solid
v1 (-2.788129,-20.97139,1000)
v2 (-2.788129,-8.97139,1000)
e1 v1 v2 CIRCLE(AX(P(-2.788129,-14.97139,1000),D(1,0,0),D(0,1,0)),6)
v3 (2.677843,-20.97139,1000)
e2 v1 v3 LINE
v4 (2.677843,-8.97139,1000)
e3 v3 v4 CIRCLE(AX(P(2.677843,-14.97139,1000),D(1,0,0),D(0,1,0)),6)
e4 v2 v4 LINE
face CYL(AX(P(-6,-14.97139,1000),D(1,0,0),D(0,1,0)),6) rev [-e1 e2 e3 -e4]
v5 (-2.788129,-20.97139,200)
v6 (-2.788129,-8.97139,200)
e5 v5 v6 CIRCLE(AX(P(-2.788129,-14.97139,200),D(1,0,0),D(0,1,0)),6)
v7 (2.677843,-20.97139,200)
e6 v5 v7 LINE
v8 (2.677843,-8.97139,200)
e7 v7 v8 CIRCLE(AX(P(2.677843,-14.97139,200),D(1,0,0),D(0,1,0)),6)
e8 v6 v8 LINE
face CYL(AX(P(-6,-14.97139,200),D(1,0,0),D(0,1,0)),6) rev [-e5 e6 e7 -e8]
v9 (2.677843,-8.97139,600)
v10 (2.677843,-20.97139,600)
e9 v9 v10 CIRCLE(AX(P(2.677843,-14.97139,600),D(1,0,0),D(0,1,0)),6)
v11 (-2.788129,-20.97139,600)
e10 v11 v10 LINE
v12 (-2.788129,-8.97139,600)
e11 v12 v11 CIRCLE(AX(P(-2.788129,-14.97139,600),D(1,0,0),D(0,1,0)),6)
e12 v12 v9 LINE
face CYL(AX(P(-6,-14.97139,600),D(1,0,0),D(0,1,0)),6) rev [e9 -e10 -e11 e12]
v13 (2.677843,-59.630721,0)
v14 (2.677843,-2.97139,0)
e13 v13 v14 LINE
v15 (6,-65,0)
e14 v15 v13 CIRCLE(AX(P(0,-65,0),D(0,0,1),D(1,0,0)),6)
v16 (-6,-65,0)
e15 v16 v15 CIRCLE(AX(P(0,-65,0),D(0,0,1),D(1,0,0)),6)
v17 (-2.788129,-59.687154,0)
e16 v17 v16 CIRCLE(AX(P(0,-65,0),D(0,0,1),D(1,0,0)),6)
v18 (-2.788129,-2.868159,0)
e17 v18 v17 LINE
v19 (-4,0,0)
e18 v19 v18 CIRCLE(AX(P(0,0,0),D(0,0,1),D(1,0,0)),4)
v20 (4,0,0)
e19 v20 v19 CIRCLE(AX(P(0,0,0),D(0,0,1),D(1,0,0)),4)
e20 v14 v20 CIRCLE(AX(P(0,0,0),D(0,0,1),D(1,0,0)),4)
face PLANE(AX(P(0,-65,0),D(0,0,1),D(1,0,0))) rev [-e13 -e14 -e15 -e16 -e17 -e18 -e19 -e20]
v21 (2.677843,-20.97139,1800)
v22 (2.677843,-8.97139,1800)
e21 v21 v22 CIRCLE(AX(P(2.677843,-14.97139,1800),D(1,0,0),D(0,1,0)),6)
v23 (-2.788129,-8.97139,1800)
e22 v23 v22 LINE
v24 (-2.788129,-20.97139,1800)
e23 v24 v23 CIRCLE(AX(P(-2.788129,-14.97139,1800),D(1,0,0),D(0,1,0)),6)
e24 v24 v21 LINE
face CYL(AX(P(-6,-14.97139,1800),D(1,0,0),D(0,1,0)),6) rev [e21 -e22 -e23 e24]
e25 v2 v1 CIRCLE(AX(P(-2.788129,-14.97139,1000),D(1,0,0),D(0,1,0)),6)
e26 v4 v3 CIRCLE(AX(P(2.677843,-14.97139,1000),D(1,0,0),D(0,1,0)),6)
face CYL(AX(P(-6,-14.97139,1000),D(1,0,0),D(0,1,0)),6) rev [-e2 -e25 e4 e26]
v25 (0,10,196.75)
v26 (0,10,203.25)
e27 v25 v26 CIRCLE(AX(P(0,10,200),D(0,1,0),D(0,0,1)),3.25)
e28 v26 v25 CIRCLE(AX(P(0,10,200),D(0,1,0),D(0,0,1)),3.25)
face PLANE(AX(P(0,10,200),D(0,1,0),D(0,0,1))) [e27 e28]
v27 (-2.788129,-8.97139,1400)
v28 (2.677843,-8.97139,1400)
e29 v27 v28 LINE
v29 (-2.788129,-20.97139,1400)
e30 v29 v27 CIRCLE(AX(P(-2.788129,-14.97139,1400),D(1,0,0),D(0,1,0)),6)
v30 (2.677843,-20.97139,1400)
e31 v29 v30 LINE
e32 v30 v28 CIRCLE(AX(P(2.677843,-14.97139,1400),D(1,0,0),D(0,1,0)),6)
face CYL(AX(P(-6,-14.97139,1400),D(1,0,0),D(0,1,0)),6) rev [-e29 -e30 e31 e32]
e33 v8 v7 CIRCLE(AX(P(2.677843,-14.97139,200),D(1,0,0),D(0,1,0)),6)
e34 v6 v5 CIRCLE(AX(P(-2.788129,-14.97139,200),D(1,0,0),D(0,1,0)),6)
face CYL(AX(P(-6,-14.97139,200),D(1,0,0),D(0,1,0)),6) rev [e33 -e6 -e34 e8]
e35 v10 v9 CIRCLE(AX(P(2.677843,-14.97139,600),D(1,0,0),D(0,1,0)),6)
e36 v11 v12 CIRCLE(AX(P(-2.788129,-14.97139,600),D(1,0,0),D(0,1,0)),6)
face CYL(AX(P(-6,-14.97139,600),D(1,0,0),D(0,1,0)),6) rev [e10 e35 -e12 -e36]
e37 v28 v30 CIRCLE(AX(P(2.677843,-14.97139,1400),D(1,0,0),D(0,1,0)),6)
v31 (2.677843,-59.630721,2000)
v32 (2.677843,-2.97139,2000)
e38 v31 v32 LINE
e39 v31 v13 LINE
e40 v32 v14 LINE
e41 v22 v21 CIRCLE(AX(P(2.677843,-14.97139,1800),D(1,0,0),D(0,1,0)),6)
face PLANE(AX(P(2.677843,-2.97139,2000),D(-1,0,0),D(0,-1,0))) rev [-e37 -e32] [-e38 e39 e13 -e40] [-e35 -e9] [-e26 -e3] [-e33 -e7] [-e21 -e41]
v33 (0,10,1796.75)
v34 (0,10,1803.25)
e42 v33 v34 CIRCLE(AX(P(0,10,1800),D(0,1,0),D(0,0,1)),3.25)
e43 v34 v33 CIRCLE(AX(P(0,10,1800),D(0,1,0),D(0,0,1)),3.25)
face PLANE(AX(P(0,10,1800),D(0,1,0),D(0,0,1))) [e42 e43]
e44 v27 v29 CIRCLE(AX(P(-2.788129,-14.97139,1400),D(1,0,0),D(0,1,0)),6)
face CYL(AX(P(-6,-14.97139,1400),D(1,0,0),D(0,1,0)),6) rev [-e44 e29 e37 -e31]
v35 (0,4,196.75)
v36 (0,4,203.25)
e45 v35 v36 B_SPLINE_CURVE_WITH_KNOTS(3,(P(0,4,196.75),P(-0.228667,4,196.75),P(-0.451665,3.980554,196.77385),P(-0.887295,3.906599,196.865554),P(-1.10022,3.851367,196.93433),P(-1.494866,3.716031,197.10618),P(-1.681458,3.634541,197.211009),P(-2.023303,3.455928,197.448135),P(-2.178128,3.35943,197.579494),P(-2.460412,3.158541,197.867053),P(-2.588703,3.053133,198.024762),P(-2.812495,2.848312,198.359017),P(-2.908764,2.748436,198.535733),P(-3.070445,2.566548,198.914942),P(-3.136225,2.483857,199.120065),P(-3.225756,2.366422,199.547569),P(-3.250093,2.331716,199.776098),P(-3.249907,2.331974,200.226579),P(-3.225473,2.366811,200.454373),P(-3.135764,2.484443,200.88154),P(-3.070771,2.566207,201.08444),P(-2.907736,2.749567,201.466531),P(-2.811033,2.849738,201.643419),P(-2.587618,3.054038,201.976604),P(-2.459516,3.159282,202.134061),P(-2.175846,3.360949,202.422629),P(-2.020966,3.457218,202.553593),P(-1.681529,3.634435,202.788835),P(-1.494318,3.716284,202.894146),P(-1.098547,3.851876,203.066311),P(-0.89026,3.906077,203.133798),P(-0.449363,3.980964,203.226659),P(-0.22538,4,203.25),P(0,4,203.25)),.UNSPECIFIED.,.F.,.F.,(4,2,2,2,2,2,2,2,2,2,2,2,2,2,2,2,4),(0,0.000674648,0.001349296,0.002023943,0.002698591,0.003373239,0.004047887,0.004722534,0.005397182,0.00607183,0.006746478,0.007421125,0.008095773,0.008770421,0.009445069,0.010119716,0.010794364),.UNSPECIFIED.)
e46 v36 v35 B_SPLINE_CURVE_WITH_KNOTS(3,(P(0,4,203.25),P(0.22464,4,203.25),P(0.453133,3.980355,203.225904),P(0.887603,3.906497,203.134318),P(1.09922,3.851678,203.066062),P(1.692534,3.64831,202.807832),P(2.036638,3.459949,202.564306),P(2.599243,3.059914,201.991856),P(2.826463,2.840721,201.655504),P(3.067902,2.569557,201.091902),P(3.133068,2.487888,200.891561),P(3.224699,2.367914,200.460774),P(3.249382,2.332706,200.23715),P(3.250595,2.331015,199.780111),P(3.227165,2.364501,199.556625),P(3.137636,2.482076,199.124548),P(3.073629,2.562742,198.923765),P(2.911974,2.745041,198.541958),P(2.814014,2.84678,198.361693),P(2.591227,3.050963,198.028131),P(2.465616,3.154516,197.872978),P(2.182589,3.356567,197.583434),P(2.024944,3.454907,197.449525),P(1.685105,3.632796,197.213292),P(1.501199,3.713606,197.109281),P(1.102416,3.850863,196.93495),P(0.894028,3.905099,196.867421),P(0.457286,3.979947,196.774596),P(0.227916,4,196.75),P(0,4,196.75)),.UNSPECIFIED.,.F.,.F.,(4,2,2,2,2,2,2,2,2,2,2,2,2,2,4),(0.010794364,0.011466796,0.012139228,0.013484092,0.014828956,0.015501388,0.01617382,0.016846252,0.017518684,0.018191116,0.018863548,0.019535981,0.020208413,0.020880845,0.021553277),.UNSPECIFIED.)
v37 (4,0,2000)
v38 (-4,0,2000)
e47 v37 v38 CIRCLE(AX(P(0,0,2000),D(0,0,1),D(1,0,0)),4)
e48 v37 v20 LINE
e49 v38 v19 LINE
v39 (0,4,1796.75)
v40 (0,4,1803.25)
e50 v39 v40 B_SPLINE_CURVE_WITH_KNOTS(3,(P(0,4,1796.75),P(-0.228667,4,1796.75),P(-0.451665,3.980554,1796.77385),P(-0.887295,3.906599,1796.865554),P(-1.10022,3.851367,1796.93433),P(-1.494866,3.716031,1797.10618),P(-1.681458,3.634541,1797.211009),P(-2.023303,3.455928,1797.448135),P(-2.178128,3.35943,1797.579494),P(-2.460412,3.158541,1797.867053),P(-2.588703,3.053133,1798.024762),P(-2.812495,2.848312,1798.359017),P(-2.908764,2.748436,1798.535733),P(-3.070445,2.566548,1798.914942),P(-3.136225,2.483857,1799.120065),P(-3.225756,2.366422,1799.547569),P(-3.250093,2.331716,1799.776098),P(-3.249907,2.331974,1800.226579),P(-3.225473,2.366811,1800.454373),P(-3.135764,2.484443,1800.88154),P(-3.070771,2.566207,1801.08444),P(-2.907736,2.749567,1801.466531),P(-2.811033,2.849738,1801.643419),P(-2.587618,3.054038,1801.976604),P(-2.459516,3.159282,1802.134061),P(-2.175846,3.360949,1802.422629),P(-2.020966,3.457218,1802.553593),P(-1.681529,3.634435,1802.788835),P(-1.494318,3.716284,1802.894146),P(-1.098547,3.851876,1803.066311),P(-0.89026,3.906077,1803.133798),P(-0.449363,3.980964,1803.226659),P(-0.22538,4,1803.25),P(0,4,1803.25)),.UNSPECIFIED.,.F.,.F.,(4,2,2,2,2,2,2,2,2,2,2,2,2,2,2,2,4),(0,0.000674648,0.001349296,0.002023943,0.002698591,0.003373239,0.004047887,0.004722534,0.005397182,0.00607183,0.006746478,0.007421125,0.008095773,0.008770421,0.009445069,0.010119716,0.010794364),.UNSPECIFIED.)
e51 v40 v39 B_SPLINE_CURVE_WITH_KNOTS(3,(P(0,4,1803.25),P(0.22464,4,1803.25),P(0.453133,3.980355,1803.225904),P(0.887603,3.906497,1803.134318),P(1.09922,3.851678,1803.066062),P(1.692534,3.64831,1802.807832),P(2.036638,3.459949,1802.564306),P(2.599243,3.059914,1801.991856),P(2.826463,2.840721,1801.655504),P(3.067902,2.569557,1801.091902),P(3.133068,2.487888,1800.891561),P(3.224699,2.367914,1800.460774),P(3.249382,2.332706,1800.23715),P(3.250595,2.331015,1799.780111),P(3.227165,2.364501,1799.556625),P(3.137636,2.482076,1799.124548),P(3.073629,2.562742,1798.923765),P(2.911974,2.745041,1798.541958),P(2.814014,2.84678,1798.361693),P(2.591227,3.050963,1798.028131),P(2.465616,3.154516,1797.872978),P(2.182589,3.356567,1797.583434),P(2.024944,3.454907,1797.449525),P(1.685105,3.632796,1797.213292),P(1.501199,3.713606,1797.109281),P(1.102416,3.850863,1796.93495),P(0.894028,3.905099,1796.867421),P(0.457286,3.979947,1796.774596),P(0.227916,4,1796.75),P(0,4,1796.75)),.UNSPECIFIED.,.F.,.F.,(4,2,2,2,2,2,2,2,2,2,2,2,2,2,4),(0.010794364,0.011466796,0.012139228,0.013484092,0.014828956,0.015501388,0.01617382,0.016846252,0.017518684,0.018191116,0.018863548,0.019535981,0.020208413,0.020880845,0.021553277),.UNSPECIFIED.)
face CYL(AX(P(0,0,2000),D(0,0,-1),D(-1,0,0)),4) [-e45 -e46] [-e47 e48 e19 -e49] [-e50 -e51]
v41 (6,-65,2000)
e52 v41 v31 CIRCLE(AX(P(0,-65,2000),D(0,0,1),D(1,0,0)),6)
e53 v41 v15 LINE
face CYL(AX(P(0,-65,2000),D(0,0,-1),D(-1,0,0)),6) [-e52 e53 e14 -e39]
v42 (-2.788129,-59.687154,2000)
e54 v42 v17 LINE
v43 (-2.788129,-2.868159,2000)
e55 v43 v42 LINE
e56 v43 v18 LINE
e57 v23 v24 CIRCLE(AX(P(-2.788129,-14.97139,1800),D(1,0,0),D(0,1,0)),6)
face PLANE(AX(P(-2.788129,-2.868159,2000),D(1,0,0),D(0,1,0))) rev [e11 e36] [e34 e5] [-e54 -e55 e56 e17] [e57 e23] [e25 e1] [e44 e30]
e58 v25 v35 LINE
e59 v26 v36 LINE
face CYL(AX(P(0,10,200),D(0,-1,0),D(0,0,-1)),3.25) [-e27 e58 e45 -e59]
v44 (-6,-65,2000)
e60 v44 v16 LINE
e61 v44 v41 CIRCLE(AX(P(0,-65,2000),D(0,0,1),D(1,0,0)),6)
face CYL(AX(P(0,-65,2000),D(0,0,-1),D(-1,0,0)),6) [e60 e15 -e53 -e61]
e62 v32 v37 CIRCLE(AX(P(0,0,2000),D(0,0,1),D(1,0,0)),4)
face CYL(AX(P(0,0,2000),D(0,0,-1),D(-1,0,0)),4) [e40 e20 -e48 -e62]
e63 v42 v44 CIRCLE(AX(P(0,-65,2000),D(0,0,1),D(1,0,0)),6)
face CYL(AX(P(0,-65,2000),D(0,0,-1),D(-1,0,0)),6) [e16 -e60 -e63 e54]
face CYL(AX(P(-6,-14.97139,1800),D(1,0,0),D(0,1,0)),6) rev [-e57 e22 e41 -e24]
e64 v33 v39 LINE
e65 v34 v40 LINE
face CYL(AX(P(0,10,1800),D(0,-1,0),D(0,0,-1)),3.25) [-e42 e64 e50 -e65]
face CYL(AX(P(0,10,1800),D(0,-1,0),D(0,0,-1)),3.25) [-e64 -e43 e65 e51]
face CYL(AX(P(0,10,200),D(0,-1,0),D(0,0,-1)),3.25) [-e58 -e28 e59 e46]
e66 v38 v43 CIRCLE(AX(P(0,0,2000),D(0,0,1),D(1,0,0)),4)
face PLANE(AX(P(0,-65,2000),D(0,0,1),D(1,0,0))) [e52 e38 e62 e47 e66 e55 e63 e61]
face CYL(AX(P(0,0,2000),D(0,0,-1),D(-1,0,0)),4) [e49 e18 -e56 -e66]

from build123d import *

# Parameters (mm, degrees)
BOSS_EXTRUDE1_DEPTH = 2000
SKETCH2_R           = 6
CUT_EXTRUDE1_DEPTH  = 2002.278667491
SKETCH3_R           = 3.25
BOSS_EXTRUDE2_DEPTH = 10


with BuildPart() as part:
    # Sketch1 → Boss-Extrude1 (new body)
    with BuildSketch(Plane.XY):
        with BuildLine():
            Line((-2.78812886, -2.868159246), (-2.78812886, -59.687153545))
            ThreePointArc((-2.78812886, -59.687153545), (0.061942892, -70.999680248), (2.677842692, -59.630720857))
            Line((2.677842692, -59.630720857), (2.677842692, -2.971389998))
            ThreePointArc((2.677842692, -2.971389998), (0.075530833, 3.999286823), (-2.78812886, -2.868159246))
        make_face()
    extrude(amount=BOSS_EXTRUDE1_DEPTH)

    # Sketch2 → Cut-Extrude1 (cut, through all)
    with BuildSketch(Plane(origin=(2.677842692, 0, 0), x_dir=(0, 0, -1), z_dir=(1, 0, 0))):
        with Locations(Location((-200, -14.971389998, 0), (0, 0, 90))):
            Circle(SKETCH2_R)
        with Locations(Location((-600, -14.971389998, 0), (0, 0, 90))):
            Circle(SKETCH2_R)
        with Locations(Location((-1000, -14.971389998, 0), (0, 0, 90))):
            Circle(SKETCH2_R)
        with Locations(Location((-1400, -14.971389998, 0), (0, 0, 90))):
            Circle(SKETCH2_R)
        with Locations(Location((-1800, -14.971389998, 0), (0, 0, 90))):
            Circle(SKETCH2_R)
    extrude(amount=-CUT_EXTRUDE1_DEPTH, mode=Mode.SUBTRACT)

    # Sketch3 → Boss-Extrude2 (add)
    with BuildSketch(Plane(origin=(0, 0, 0), x_dir=(1, 0, 0), z_dir=(0, 1, 0))):
        with Locations(Location((0, -200, 0), (0, 0, 90))):
            Circle(SKETCH3_R)
        with Locations(Location((0, -1800, 0), (0, 0, 90))):
            Circle(SKETCH3_R)
    extrude(amount=BOSS_EXTRUDE2_DEPTH)


solid = part.part
